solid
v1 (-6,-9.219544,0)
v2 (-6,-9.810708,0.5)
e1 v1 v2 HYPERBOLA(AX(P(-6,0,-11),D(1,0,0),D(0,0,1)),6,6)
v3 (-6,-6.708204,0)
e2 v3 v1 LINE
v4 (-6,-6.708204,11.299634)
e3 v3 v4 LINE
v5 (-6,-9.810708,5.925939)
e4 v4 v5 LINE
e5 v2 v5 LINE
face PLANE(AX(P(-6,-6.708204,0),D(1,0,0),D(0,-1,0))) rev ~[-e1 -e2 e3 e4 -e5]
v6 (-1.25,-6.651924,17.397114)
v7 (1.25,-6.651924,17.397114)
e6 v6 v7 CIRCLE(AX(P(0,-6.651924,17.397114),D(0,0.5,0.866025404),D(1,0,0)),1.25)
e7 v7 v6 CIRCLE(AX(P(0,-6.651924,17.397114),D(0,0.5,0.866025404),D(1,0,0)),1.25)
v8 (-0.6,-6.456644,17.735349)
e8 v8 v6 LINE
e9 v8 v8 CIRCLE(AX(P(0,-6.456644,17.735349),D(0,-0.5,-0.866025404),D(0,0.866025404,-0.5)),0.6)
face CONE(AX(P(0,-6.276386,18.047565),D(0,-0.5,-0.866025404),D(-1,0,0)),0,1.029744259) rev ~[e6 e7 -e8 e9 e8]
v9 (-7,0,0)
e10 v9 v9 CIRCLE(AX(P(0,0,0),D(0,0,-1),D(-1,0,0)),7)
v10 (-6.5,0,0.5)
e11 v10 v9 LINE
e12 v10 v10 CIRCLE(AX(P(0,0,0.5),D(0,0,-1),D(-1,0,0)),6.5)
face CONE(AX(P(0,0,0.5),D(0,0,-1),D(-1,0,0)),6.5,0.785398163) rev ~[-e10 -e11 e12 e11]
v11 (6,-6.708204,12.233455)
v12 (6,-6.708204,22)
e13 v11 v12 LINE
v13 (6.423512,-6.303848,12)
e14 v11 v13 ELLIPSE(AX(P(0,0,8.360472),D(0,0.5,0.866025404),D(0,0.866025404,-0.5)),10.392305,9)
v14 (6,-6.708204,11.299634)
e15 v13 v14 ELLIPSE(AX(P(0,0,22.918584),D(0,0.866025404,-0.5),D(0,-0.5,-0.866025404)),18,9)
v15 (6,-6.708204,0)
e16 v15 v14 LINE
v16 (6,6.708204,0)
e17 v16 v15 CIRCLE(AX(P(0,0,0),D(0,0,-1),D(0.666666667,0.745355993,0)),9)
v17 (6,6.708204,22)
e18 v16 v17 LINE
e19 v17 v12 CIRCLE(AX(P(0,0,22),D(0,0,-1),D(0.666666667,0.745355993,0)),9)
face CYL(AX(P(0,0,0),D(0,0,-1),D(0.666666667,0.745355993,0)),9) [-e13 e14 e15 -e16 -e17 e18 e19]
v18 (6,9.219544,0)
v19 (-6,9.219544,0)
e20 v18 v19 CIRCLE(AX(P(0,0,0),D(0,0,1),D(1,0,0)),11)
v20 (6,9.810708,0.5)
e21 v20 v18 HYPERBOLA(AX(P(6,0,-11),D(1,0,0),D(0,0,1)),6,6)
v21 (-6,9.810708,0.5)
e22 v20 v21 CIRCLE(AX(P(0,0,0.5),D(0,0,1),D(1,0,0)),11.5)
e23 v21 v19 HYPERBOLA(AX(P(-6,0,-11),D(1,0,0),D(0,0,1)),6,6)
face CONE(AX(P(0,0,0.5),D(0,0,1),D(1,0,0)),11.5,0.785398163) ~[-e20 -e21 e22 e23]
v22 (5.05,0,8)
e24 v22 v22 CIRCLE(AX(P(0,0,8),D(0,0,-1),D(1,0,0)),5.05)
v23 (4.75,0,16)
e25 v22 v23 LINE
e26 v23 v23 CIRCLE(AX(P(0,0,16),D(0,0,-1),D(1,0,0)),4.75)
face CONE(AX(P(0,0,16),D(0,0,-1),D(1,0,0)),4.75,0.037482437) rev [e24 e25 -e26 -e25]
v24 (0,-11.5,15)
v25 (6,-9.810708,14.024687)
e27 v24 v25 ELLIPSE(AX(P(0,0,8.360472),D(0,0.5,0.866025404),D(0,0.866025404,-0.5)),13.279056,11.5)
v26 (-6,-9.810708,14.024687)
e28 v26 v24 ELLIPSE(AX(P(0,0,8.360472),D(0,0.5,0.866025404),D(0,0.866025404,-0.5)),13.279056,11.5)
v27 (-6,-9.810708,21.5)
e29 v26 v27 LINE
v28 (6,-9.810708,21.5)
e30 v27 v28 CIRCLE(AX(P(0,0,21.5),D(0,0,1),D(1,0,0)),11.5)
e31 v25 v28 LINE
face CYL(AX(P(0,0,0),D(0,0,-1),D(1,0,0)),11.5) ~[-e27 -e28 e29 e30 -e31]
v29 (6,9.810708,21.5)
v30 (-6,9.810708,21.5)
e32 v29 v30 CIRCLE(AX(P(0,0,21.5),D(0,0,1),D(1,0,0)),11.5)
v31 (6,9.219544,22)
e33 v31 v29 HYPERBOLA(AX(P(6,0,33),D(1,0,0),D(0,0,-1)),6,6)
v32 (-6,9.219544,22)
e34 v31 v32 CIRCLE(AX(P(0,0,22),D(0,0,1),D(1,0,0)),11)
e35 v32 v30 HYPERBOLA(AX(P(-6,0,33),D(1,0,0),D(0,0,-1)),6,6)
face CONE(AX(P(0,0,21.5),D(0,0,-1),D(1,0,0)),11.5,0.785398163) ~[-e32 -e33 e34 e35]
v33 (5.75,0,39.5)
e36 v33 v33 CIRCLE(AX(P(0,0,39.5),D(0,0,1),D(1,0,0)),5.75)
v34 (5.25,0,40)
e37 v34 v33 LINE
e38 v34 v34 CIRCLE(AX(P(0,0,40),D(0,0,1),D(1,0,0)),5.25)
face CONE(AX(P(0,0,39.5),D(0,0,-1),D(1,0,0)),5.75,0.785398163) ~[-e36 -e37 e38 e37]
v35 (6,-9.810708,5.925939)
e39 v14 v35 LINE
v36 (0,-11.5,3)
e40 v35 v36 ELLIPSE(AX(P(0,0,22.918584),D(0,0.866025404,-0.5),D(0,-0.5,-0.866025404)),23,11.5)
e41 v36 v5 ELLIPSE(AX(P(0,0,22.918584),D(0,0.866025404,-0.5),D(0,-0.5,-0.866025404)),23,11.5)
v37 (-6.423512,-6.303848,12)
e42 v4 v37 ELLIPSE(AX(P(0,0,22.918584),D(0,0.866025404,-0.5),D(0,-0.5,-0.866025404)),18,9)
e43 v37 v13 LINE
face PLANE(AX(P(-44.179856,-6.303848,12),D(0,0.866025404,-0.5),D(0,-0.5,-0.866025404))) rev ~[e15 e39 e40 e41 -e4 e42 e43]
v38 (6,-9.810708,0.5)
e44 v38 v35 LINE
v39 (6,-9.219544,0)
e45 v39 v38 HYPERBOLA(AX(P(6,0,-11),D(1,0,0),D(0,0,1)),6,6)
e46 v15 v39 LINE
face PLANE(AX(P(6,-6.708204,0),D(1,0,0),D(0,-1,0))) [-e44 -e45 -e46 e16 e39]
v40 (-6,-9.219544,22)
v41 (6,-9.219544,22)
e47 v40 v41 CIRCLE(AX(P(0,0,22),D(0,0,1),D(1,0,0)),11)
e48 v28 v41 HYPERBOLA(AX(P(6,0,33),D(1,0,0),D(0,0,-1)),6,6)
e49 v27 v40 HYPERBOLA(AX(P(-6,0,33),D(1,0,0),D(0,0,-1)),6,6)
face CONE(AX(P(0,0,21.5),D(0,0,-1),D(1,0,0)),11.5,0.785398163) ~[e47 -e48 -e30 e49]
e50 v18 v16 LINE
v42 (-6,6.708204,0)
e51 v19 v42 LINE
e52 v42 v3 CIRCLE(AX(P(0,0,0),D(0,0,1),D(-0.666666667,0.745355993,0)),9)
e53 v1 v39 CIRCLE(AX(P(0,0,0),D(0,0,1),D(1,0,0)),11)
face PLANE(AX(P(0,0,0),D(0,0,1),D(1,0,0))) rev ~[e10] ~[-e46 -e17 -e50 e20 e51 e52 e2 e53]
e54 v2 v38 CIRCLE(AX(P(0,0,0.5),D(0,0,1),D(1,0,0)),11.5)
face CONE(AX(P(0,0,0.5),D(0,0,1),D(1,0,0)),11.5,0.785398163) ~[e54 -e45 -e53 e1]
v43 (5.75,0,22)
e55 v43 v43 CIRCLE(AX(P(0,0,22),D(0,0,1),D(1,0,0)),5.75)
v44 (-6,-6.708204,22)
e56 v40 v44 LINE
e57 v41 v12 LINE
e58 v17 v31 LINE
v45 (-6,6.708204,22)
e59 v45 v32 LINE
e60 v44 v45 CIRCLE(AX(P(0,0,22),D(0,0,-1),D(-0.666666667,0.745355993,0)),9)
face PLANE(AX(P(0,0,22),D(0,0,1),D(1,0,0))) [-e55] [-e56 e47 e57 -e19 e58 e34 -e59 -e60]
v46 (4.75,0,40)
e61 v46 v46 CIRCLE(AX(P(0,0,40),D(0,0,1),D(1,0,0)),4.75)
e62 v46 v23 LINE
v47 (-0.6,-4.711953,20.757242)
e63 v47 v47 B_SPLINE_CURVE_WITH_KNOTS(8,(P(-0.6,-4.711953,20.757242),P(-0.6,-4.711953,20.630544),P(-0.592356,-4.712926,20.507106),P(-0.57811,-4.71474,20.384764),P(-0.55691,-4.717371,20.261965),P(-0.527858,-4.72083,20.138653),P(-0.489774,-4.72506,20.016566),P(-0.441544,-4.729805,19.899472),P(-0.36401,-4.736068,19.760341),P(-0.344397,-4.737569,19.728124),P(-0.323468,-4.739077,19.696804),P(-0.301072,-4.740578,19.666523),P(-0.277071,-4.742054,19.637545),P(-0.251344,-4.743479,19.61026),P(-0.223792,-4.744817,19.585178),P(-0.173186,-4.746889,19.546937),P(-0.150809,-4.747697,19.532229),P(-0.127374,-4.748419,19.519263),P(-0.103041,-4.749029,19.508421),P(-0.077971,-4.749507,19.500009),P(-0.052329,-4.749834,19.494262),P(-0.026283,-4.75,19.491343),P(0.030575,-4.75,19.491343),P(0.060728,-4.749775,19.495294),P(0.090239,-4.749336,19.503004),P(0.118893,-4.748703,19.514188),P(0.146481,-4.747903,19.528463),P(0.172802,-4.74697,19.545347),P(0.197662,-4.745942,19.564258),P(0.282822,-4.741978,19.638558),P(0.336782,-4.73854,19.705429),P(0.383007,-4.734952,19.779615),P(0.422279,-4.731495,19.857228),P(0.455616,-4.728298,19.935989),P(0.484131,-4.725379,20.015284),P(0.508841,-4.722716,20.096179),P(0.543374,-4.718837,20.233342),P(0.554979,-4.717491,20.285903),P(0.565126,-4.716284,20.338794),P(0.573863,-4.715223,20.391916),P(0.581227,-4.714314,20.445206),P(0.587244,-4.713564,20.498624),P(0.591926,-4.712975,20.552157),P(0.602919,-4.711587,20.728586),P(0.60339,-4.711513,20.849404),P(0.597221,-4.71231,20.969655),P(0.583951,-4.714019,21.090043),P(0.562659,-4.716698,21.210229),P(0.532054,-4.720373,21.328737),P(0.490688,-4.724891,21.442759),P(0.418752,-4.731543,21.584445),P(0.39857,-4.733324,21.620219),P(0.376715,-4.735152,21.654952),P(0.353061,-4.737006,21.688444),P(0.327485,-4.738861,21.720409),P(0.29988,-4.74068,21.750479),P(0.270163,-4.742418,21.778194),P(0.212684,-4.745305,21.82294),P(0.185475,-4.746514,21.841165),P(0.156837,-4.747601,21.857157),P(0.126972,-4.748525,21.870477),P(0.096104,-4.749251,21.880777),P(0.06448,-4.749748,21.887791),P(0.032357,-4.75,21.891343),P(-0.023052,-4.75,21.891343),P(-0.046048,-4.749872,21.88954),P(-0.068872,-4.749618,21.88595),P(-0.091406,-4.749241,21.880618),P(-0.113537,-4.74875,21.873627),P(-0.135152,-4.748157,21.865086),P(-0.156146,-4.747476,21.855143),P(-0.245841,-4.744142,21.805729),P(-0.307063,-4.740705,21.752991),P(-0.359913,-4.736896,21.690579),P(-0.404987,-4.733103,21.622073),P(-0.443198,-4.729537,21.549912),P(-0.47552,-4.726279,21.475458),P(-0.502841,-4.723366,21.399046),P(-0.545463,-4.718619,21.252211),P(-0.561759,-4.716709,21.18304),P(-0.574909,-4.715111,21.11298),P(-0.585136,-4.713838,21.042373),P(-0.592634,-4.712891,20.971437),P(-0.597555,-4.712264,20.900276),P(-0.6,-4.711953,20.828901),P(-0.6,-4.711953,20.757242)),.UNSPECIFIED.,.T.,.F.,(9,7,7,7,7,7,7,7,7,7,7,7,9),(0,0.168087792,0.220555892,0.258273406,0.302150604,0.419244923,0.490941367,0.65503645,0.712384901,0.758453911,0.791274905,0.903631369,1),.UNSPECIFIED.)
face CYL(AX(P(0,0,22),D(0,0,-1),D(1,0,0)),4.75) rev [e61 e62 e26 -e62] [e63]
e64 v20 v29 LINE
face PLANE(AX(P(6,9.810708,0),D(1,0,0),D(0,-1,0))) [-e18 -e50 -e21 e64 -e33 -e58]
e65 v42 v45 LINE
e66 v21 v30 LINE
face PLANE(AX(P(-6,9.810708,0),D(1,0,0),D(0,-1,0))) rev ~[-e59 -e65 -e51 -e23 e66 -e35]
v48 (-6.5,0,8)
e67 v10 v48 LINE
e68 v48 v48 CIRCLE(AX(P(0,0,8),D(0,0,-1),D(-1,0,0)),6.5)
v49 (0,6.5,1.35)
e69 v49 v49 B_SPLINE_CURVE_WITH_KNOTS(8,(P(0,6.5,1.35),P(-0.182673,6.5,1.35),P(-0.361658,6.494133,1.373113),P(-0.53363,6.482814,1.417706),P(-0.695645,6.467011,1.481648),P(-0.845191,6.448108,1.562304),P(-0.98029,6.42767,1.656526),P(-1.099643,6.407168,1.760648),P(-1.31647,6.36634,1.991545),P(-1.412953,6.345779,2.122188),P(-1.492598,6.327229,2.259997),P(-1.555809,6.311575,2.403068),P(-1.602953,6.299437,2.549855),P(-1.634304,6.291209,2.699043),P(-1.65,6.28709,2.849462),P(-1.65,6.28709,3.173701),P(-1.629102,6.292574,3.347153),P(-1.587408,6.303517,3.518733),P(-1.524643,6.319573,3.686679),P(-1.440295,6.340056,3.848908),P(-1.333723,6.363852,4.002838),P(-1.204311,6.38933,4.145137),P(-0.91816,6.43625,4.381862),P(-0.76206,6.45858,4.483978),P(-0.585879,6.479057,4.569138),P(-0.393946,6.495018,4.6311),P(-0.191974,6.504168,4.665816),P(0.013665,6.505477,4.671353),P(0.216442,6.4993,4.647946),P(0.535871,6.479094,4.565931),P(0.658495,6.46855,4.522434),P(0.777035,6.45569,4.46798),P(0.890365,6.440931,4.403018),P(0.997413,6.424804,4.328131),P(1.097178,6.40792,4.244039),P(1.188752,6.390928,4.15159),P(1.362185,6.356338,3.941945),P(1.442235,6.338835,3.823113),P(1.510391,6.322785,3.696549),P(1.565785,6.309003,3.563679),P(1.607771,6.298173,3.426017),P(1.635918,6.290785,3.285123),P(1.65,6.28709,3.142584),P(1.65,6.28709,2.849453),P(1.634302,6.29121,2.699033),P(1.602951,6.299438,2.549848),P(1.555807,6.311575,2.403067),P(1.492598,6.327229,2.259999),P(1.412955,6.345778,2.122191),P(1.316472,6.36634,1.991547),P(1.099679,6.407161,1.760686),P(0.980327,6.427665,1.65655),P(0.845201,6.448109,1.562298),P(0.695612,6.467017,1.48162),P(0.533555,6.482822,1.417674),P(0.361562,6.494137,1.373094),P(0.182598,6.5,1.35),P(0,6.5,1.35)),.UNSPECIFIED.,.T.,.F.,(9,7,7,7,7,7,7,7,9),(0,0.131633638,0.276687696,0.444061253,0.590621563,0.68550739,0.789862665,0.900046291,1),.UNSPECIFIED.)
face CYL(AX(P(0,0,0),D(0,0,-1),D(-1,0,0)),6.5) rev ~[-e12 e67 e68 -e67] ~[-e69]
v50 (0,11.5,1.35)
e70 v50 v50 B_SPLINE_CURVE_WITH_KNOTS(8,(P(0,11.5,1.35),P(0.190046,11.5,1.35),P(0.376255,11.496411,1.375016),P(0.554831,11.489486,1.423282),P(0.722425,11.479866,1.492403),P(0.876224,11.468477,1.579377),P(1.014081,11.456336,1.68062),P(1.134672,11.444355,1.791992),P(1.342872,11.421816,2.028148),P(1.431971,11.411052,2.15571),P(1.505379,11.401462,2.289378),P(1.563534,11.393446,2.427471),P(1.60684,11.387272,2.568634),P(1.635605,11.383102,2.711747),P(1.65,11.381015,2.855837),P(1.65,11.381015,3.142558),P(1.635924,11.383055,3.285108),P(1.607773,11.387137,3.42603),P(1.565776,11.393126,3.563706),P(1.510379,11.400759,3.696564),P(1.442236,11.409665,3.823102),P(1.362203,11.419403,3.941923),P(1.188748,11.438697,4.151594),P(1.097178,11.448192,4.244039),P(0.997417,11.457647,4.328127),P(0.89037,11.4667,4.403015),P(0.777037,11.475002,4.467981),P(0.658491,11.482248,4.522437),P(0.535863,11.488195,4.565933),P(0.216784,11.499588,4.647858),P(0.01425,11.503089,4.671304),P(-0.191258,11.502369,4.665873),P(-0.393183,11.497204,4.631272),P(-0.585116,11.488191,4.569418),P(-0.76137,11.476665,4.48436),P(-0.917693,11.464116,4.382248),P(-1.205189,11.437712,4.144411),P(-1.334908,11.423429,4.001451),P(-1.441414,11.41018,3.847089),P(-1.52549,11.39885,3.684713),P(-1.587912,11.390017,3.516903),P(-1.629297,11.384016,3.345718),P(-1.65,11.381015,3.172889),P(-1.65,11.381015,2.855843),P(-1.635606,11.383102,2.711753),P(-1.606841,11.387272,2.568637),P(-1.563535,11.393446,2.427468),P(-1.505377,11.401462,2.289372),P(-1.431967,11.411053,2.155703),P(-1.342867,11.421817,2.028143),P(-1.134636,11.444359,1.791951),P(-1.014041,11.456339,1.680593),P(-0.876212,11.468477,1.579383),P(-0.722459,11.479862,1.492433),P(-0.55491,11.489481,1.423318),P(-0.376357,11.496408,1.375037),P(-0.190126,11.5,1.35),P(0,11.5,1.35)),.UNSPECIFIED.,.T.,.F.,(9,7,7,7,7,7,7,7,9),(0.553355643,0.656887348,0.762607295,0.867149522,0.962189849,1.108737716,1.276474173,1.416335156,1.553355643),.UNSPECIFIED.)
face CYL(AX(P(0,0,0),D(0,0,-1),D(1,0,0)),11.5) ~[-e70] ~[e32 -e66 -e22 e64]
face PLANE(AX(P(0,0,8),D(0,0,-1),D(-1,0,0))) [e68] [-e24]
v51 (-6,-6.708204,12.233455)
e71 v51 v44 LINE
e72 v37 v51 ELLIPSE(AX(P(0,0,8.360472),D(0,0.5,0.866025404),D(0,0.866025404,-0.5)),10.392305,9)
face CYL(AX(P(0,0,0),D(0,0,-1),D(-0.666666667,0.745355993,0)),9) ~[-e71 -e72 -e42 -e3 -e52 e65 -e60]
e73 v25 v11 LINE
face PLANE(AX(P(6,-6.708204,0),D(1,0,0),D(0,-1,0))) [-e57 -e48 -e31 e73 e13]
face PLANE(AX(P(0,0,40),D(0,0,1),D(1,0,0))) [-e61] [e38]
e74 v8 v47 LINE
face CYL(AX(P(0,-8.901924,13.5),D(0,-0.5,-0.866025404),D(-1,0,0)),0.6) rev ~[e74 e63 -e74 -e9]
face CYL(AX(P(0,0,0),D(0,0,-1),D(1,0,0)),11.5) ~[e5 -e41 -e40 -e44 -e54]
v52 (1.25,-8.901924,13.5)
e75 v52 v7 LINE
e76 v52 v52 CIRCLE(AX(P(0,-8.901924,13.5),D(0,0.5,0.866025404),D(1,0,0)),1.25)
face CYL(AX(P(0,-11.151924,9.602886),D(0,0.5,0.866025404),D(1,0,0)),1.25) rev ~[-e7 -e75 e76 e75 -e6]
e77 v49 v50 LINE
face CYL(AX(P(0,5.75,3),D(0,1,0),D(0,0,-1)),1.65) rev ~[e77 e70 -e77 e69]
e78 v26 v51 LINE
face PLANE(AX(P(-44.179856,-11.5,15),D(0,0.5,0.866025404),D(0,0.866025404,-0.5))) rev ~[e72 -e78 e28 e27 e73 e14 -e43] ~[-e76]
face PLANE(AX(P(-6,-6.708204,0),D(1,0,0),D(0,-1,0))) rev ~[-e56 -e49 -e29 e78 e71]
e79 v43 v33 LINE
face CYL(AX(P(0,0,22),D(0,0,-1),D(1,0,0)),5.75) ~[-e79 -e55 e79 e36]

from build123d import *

# Parameters (mm, degrees)
SKETCH1_R                       = 11.5
SKETCH1_R_2                     = 4.75
BOSS_EXTRUDE1_DEPTH             = 22
SKETCH2_R                       = 5.75
SKETCH2_R_2                     = 4.75
BOSS_EXTRUDE2_DEPTH             = 18
SKETCH3_R                       = 6.5
CUT_EXTRUDE1_DEPTH              = 8
CHAMFER1_SIZE                   = 0.5
SKETCH12_W                      = 1.65
SKETCH12_H                      = 11.5
CUT_EXTRUDE4_DEPTH              = 44.179856468
CUT_EXTRUDE4_DEPTH_BACK         = 44.179856468
F_1_2_1_2_DIAMETER_HOLE1_REACH  = 40.711
F_1_2_1_2_DIAMETER_HOLE1_BORE_R = 0.6
M3_TAPPED_HOLE2_D               = 2.5
M3_TAPPED_HOLE2_DEPTH           = 4.5
M3_TAPPED_HOLE2_TIP             = 0.751075774
CHAMFER2_SIZE                   = 0.3
CHAMFER2_SIZE2                  = 8
CUT_EXTRUDE5_DEPTH              = 44.179856561
CHAMFER3_SIZE                   = 0.5


with BuildPart() as part:
    # Sketch1 → Boss-Extrude1 (new body)
    with BuildSketch(Plane.XY):
        Circle(SKETCH1_R)
        Circle(SKETCH1_R_2, mode=Mode.SUBTRACT)
    extrude(amount=BOSS_EXTRUDE1_DEPTH)

    # Sketch2 → Boss-Extrude2 (add)
    with BuildSketch(Plane.XY.offset(22)):
        Circle(SKETCH2_R)
        Circle(SKETCH2_R_2, mode=Mode.SUBTRACT)
    extrude(amount=BOSS_EXTRUDE2_DEPTH)

    # Sketch3 → Cut-Extrude1 (cut)
    with BuildSketch(Plane(origin=(0, 0, 0), x_dir=(-1, 0, 0), z_dir=(0, 0, -1))):
        Circle(SKETCH3_R)
    extrude(amount=-CUT_EXTRUDE1_DEPTH, mode=Mode.SUBTRACT)

    # Chamfer1
    chamfer1_edges = [part.edges().sort_by_distance(p)[0] for p in [
        (-11.5, 0, 0),
        (-11.5, 0, 22),
    ]]
    chamfer(chamfer1_edges, length=CHAMFER1_SIZE)

    # Sketch12 → M4 Tapped Hole3 (revolve, cut)
    with BuildSketch(Plane(origin=(0, 0, 3), x_dir=(0, 0, -1), z_dir=(1, 0, 0))):
        with Locations((0.825, 5.75)):
            Rectangle(SKETCH12_W, SKETCH12_H)
    revolve(axis=Axis((0, -6.35, 3), (0, 1, 0)), mode=Mode.SUBTRACT)

    # Sketch14 → Cut-Extrude4 (cut, two sides: drawn at the far end of the back side and taken through both)
    with BuildSketch(Plane(origin=(0, 0, 0), x_dir=(0, 0, -1), z_dir=(1, 0, 0)).offset(-CUT_EXTRUDE4_DEPTH_BACK)):
        Polygon((-15, -11.5), (-12, -6.303847577), (-3, -11.5), align=None)
    extrude(amount=CUT_EXTRUDE4_DEPTH + CUT_EXTRUDE4_DEPTH_BACK, mode=Mode.SUBTRACT)

    # Ø1.2 (1.2) Diameter Hole1 bore → Ø1.2 (1.2) Diameter Hole1 (cut, up to next)
    with BuildSketch(Plane(origin=(0, 3.620190528, 6.270353928), x_dir=(-1, 0, 0), z_dir=(0, -0.5000000000000001, -0.8660254037844386)), mode=Mode.PRIVATE) as f_1_2_1_2_diameter_hole1_sk1:
        with Locations((0, -14.459292144)):
            Circle(F_1_2_1_2_DIAMETER_HOLE1_BORE_R)
    f_1_2_1_2_diameter_hole1_tool1 = extrude(f_1_2_1_2_diameter_hole1_sk1.sketch, amount=-F_1_2_1_2_DIAMETER_HOLE1_REACH, mode=Mode.PRIVATE) & part.part
    add(f_1_2_1_2_diameter_hole1_tool1.solids().sort_by_distance((0, -8.901924, 13.5))[0], mode=Mode.SUBTRACT)

    # M3 Tapped Hole2
    with Locations(Plane(origin=(0, 3.620190528, 6.270353928), x_dir=(-1, 0, 0), z_dir=(0, -0.5000000000000001, -0.8660254037844386))):
        with Locations((0, -14.459292144)):
            Hole(M3_TAPPED_HOLE2_D / 2, depth=M3_TAPPED_HOLE2_DEPTH)
            with Locations((0, 0, -(M3_TAPPED_HOLE2_DEPTH + M3_TAPPED_HOLE2_TIP / 2))):  # 118° drill point
                Cone(0, M3_TAPPED_HOLE2_D / 2, M3_TAPPED_HOLE2_TIP, mode=Mode.SUBTRACT)

    # Chamfer2
    chamfer2_edges = [part.edges().sort_by_distance(p)[0] for p in [
        (-4.75, 0, 8),
    ]]
    chamfer2_side = [part.faces().sort_by_distance(p)[0] for p in [
        (6.316152237, 0, 8),
    ]]
    chamfer(chamfer2_edges, length=CHAMFER2_SIZE, length2=CHAMFER2_SIZE2, reference=chamfer2_side[0])

    # Sketch19 → Cut-Extrude5 (cut, through all)
    with BuildSketch(Plane(origin=(0, 0, 0), x_dir=(-1, 0, 0), z_dir=(0, 0, -1))):
        with BuildLine():
            Line((-6, 9.810708435), (-6, 6.708203932))
            ThreePointArc((-6, 6.708203932), (-9, 0), (-6, -6.708203932))
            Line((-6, -6.708203932), (-6, -9.810708435))
            ThreePointArc((-6, -9.810708435), (-11.5, 0), (-6, 9.810708435))
        make_face()
        with BuildLine():
            Line((6, 9.810708435), (6, 6.708203932))
            ThreePointArc((6, 6.708203932), (9, 0), (6, -6.708203932))
            Line((6, -6.708203932), (6, -9.810708435))
            ThreePointArc((6, -9.810708435), (11.5, 0), (6, 9.810708435))
        make_face()
    extrude(amount=-CUT_EXTRUDE5_DEPTH, mode=Mode.SUBTRACT)

    # Chamfer3
    chamfer3_edges = [part.edges().sort_by_distance(p)[0] for p in [
        (-5.75, 0, 40),
        (6.5, 0, 0),
    ]]
    chamfer(chamfer3_edges, length=CHAMFER3_SIZE)


solid = part.part
